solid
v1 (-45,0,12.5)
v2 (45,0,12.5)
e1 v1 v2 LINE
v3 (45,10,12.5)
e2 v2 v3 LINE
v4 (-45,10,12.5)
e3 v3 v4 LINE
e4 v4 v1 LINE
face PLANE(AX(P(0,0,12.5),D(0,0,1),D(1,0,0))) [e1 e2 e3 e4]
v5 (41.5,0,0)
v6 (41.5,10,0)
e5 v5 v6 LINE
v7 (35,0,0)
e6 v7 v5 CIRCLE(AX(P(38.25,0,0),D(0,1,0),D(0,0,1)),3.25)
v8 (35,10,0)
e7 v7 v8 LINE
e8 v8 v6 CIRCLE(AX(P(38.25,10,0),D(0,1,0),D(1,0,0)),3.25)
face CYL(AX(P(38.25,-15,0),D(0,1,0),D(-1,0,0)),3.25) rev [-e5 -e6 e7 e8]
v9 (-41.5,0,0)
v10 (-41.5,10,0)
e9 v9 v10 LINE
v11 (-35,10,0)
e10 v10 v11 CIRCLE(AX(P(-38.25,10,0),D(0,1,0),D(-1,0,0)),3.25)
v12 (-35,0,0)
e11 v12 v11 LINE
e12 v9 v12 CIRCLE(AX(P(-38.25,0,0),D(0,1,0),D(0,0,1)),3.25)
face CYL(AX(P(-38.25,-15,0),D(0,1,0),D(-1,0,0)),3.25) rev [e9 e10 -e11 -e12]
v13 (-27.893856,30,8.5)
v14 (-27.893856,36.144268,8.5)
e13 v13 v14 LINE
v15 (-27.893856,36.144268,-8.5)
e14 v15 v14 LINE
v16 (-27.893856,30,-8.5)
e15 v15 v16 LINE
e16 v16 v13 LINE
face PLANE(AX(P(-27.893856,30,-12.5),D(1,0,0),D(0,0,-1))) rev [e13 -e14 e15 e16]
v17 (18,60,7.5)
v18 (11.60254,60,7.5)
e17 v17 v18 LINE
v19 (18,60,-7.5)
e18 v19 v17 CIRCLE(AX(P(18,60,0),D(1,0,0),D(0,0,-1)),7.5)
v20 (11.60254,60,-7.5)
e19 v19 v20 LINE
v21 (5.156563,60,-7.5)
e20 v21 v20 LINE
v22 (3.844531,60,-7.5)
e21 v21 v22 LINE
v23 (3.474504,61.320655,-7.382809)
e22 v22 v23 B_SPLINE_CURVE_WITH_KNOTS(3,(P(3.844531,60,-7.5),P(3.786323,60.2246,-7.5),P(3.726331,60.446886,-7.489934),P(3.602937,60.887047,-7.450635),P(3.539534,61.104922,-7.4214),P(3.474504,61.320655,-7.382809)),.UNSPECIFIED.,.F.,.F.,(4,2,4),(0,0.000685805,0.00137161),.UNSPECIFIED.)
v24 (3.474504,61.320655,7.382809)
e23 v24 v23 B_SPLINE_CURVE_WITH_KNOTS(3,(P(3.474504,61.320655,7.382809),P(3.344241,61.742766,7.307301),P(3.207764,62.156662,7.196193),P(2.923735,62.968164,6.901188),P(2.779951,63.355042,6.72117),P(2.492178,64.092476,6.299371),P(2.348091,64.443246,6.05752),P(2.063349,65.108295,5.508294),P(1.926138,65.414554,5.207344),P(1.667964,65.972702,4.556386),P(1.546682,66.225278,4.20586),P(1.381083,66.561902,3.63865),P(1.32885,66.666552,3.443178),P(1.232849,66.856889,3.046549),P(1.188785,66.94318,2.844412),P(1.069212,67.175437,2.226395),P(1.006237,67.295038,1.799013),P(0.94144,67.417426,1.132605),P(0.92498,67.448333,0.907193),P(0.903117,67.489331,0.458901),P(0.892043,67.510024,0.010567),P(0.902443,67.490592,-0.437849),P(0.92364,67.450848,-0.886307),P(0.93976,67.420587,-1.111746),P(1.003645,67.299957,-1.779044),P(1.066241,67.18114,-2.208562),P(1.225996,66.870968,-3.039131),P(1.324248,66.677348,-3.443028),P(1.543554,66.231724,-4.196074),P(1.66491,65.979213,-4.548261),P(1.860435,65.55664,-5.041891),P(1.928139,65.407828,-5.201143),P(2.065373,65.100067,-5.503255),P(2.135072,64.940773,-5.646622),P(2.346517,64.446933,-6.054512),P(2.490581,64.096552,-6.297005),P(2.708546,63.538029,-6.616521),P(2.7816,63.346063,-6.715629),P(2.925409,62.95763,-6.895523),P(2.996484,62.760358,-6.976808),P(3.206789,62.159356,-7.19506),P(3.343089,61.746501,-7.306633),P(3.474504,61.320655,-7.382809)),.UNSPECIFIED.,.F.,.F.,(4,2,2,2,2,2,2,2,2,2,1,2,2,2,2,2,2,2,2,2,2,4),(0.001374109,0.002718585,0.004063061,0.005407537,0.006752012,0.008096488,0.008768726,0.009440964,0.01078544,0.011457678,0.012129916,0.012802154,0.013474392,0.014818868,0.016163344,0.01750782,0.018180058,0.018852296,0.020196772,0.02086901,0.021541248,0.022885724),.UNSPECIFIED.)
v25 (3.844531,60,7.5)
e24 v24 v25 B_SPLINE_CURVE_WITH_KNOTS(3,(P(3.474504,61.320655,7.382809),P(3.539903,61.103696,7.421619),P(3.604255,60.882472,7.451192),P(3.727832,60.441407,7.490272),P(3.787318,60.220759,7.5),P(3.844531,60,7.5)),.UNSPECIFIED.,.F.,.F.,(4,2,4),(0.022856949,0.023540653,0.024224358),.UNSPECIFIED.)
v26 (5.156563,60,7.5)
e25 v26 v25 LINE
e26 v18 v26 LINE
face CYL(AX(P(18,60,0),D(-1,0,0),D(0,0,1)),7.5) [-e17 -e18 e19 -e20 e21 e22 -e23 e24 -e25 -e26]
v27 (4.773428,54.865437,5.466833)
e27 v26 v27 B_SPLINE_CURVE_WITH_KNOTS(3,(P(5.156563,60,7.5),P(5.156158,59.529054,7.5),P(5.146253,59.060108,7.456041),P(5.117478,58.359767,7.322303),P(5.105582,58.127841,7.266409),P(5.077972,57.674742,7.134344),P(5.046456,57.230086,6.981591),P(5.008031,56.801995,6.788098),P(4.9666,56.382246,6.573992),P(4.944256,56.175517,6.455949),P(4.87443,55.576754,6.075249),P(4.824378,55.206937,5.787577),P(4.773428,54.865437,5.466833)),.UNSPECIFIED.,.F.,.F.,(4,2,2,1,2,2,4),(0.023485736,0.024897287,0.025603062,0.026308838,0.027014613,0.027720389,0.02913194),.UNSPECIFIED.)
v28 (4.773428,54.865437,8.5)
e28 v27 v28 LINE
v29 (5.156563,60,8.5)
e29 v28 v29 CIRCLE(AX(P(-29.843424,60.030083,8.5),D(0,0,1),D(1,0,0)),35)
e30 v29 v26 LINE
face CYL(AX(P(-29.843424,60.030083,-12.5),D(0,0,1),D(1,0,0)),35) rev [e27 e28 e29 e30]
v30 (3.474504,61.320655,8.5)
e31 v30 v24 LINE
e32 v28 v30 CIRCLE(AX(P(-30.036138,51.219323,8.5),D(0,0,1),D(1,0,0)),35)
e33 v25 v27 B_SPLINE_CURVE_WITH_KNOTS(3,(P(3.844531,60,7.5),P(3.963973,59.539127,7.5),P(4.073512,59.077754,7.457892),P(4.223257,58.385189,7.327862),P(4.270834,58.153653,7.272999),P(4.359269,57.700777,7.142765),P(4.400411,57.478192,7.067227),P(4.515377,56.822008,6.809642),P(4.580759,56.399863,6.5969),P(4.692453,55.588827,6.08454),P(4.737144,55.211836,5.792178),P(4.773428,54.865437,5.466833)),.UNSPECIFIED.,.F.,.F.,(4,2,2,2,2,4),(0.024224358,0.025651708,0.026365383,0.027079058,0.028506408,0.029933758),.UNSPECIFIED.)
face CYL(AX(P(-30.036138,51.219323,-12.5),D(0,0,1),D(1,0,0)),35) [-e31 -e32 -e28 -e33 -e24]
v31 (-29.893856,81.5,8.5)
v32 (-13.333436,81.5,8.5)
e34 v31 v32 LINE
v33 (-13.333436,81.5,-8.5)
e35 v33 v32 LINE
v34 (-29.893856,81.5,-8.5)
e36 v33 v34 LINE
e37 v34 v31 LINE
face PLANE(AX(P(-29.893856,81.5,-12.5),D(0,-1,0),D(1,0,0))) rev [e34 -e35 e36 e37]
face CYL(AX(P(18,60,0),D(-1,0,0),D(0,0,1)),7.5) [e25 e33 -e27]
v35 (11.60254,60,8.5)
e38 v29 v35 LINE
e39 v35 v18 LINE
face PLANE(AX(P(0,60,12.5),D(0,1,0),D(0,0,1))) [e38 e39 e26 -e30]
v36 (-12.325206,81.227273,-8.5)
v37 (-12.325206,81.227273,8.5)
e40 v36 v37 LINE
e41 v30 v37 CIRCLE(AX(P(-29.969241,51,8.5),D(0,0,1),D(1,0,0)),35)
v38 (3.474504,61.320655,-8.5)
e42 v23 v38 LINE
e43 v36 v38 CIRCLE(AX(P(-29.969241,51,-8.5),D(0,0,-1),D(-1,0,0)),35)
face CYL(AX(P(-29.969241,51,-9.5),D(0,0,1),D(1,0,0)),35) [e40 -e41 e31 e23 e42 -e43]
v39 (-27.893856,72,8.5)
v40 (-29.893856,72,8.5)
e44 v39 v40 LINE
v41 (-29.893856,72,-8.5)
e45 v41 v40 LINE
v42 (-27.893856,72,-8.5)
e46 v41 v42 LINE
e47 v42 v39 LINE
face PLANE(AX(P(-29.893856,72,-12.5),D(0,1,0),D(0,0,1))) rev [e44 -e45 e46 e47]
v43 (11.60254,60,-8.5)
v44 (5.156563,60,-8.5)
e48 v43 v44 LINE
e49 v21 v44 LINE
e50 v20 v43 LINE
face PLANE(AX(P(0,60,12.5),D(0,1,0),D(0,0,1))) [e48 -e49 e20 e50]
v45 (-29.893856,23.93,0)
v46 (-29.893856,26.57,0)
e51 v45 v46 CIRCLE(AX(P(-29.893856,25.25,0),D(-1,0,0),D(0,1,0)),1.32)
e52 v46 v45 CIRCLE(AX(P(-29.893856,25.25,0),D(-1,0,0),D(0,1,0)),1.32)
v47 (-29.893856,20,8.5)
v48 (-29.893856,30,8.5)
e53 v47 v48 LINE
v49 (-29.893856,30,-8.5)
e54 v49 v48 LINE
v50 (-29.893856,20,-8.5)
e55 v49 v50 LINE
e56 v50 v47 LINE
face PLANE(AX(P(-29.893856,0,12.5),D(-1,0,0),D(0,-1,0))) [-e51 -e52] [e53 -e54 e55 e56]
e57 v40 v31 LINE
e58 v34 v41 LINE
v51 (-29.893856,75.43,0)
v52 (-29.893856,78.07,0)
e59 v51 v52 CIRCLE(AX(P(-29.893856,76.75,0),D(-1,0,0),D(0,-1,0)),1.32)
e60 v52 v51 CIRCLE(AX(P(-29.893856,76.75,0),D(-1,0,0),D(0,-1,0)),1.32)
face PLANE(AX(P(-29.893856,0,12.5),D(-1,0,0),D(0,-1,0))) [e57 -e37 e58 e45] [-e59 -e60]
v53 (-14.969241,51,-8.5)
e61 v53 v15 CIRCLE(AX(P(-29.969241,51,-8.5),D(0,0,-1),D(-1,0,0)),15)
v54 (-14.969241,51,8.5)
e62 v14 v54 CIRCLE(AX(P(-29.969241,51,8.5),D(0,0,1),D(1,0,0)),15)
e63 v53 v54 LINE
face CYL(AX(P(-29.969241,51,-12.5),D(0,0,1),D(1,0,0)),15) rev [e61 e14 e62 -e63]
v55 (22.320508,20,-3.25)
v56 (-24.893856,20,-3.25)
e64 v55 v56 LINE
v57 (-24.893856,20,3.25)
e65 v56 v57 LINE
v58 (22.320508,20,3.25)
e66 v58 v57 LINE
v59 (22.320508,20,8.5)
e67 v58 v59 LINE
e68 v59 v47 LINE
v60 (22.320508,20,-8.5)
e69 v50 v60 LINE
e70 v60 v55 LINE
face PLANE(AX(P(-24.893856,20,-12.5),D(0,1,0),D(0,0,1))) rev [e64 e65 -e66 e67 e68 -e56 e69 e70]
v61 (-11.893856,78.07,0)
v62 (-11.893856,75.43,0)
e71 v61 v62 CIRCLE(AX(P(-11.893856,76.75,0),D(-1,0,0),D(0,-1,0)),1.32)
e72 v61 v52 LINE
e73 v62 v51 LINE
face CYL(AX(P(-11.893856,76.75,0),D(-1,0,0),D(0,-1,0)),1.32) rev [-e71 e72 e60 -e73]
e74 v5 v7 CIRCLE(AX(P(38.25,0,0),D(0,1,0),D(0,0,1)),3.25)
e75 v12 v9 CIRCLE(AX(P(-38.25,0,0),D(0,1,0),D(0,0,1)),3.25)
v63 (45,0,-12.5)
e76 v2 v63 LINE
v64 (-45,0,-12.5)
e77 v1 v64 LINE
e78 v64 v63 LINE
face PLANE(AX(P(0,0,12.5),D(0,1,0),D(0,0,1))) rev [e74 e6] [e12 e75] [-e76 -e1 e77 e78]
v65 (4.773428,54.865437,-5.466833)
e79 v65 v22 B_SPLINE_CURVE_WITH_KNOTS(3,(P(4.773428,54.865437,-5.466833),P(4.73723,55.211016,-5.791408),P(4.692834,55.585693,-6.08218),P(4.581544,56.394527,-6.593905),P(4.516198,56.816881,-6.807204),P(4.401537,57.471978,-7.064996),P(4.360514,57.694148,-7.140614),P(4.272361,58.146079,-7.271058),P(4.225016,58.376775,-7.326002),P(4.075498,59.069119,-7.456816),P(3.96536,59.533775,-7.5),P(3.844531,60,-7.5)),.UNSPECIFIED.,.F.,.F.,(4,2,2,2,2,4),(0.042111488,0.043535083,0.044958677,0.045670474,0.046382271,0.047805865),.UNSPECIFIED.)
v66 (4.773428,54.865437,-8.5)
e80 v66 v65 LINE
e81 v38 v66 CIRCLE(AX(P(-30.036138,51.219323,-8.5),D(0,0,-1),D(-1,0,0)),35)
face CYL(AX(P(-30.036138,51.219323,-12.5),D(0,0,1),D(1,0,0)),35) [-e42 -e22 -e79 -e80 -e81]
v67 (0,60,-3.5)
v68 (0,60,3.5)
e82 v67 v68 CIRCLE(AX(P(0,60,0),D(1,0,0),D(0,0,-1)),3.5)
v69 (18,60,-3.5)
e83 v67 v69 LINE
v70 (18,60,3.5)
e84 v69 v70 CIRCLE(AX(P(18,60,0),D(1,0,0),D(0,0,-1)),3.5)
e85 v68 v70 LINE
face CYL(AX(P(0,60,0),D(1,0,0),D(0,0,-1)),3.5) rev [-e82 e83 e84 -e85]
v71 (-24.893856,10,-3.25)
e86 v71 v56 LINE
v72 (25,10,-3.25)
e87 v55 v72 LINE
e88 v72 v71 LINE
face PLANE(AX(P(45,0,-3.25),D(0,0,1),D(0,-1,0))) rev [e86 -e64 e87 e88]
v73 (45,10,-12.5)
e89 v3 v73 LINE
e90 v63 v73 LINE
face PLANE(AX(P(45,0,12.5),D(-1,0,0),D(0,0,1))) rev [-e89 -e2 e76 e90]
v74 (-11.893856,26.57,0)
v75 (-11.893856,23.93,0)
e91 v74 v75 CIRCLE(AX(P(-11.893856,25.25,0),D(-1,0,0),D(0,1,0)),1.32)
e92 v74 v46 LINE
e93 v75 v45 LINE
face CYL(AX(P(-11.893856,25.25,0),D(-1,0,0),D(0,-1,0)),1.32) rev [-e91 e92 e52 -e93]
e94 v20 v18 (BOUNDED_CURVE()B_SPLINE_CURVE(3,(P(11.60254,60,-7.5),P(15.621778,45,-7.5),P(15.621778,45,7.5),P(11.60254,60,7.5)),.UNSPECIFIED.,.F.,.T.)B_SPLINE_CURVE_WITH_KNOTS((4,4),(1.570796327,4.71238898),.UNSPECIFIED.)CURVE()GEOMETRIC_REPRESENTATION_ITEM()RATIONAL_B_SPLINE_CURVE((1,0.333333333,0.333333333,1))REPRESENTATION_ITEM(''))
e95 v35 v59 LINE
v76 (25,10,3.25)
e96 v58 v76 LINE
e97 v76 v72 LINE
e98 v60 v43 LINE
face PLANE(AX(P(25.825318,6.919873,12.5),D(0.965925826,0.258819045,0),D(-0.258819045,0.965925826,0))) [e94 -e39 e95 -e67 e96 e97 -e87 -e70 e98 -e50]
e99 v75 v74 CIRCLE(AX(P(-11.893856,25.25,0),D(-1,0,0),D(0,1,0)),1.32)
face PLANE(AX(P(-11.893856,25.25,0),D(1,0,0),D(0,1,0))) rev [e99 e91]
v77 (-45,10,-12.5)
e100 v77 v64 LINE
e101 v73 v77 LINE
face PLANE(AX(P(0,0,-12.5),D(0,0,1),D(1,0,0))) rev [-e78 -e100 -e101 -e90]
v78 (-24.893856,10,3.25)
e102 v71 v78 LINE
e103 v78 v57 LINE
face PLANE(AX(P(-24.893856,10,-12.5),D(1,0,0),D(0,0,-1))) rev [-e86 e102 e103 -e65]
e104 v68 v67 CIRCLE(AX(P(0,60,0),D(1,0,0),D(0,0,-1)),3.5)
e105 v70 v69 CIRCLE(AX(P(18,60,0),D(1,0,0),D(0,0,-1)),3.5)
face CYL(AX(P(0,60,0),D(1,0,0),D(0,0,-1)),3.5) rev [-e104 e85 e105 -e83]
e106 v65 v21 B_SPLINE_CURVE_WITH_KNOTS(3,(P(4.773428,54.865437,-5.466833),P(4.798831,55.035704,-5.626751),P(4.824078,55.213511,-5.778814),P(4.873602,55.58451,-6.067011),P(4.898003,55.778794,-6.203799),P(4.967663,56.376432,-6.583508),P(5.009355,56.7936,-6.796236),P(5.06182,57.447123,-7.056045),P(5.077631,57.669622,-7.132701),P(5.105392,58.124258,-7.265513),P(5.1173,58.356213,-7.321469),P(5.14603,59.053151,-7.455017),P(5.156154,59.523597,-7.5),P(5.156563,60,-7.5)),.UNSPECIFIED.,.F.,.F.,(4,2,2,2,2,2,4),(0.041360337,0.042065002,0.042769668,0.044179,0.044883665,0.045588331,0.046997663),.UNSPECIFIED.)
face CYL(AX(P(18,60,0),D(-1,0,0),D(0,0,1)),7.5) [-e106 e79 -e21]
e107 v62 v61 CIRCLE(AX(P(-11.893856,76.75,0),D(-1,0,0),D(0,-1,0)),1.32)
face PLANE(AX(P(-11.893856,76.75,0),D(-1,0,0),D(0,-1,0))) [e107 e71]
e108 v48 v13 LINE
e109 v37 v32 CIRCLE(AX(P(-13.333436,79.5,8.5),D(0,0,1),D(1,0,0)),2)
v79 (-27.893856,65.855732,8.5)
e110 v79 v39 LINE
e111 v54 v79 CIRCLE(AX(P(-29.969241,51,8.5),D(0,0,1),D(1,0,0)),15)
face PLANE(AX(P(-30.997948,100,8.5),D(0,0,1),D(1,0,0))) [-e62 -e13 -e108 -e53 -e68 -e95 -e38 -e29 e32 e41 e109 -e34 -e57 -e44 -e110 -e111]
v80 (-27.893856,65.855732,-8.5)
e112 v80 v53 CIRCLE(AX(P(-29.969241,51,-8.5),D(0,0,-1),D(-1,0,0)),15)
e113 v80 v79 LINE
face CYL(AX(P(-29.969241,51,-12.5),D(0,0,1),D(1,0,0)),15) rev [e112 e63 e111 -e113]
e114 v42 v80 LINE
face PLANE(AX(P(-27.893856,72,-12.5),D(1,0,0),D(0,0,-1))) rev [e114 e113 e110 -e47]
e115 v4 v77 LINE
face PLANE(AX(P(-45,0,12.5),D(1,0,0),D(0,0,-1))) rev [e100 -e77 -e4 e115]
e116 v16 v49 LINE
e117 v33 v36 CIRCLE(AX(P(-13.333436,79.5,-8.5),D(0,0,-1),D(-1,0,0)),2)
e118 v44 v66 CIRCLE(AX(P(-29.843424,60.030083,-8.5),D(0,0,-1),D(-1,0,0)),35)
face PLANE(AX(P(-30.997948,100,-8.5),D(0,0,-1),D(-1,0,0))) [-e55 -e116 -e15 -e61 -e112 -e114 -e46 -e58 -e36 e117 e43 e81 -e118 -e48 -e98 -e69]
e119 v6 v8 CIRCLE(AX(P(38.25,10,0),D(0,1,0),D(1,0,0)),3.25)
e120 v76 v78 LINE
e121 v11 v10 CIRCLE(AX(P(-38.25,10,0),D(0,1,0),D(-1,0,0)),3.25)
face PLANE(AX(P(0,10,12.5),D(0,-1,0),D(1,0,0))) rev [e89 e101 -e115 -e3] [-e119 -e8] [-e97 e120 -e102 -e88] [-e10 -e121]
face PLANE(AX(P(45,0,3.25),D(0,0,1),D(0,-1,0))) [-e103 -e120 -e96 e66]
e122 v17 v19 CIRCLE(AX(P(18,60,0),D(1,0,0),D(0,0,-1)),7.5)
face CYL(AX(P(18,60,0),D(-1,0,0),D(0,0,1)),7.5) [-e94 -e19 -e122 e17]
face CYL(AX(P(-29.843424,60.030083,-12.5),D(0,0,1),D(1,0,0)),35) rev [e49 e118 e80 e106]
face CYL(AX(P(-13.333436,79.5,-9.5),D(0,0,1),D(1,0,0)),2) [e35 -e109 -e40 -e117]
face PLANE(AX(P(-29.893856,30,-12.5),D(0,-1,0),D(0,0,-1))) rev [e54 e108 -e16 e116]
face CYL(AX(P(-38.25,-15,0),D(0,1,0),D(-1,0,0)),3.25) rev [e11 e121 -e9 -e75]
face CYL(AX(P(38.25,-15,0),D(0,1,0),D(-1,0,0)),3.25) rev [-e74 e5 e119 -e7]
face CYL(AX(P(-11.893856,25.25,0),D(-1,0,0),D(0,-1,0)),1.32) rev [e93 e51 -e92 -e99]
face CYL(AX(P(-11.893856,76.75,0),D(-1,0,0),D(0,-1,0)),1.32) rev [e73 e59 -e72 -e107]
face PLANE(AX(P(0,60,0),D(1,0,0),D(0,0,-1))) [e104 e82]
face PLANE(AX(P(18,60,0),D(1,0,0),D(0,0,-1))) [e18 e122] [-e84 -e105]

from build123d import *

# Parameters (mm, degrees)
BRACKET_PROFILE_SKETCH_W     = 5
BRACKET_PROFILE_SKETCH_H     = 10
BRACKET_BODY_DEPTH           = 12.5
SPLIT_SLOT_SKETCH_R          = 3.25
SPLIT_SLOT_CUT_DEPTH         = 25
SIDE_TRIM_SKETCH_W           = 61.995895312
SIDE_TRIM_SKETCH_H           = 4
SIDE_TRIM_CUT_DEPTH          = 100
BASE_PLATE_SKETCH_W          = 61.995895312
BASE_PLATE_SKETCH_H          = 4
BASE_PLATE_DEPTH             = 10
UPRIGHT_STEP_CUT_DEPTH       = 104.780787142
UPRIGHT_RELIEF_SKETCH_W      = 5
UPRIGHT_RELIEF_SKETCH_H      = 10
UPRIGHT_RELIEF_CUT_DEPTH     = 96.437152095
RELIEF_NOTCH_A_SKETCH_W      = 5.25
RELIEF_NOTCH_A_SKETCH_H      = 10
RELIEF_NOTCH_A_DEPTH         = 109.090938874
RELIEF_NOTCH_B_SKETCH_W      = 5.25
RELIEF_NOTCH_B_SKETCH_H      = 10
RELIEF_NOTCH_B_DEPTH         = 109.090938874
BEARING_SEAT_CUT_DEPTH       = 96.437152095
SEAT_GROOVE_A_SKETCH_R       = 1.32
SEAT_GROOVE_A_DEPTH          = 18
SEAT_GROOVE_B_DEPTH          = 18
SIDE_BOSS_SKETCH_R           = 7.5
SIDE_BOSS_DEPTH              = 18
SIDE_BOSS_BORE_SKETCH_R      = 3.5
SIDE_BOSS_BORE_DEPTH         = 18
FACE_RECESS_CUT_DEPTH        = 94.933487193
FACE_RECESS_CUT_DEPTH_BACK   = 94.933487193
SIDE_SLOT_CUT_DEPTH          = 5
BOSS_EXTENSION_SKETCH_R      = 7.5
BOSS_EXTENSION_DEPTH         = 18
BOSS_EXTENSION_BORE_SKETCH_R = 3.5
BOSS_EXTENSION_BORE_DEPTH    = 18


with BuildPart() as part:
    # Bracket Profile Sketch → Bracket Body (new, symmetric)
    with BuildSketch(Plane.XY):
        Polygon((-45, 10), (-45, 0), (0, 0), (45, 0), (45, 10), align=None)
        with BuildLine():
            Line((-13.893855715, 10), (25, 10))
            Line((25, 10), (11.602540378, 60))
            Line((11.602540378, 60), (5.106144285, 60))
            ThreePointArc((5.106144285, 60), (-0.019117223, 41.765417471), (-13.893855715, 28.871235167))
            Line((-13.893855715, 28.871235167), (-13.893855715, 10))
        make_face()
        Polygon((-24.893855715, 10), (-13.893855715, 10), (-13.893855715, 28.871235167), (-29.893855715, 29), (-29.893855715, 20), (-24.893855715, 20), align=None)
        with Locations((-27.393855715, 15)):
            Rectangle(BRACKET_PROFILE_SKETCH_W, BRACKET_PROFILE_SKETCH_H)
        with BuildLine():
            Line((-13.893855715, 41), (-13.893855715, 28.871235167))
            ThreePointArc((-13.893855715, 28.871235167), (-0.019117223, 41.765417471), (5.106144285, 60))
            ThreePointArc((5.106144285, 60), (-0.019117223, 78.234582529), (-13.893855715, 91.128764833))
            Line((-13.893855715, 91.128764833), (-13.893855715, 79))
            Line((-13.893855715, 79), (-6.677482183, 79))
            ThreePointArc((-6.677482183, 79), (0.106144285, 60), (-6.677482183, 41))
            Line((-6.677482183, 41), (-13.893855715, 41))
        make_face()
        Polygon((-29.893855715, 29), (-13.893855715, 28.871235167), (-13.893855715, 41), (-27.893855715, 41), (-27.893855715, 39), (-29.893855715, 39), align=None)
        with BuildLine():
            Line((-27.893855715, 41), (-13.893855715, 41))
            Line((-13.893855715, 41), (-13.893855715, 79))
            Line((-13.893855715, 79), (-27.893855715, 79))
            Line((-27.893855715, 79), (-27.893855715, 74.866068747))
            ThreePointArc((-27.893855715, 74.866068747), (-14.893855715, 60), (-27.893855715, 45.133931253))
            Line((-27.893855715, 45.133931253), (-27.893855715, 41))
        make_face()
        with BuildLine():
            Line((-13.893855715, 79), (-13.893855715, 41))
            Line((-13.893855715, 41), (-6.677482183, 41))
            ThreePointArc((-6.677482183, 41), (0.106144285, 60), (-6.677482183, 79))
            Line((-6.677482183, 79), (-13.893855715, 79))
        make_face()
        with BuildLine():
            Line((-29.893855715, 60), (-29.893855715, 39))
            Line((-29.893855715, 39), (-27.893855715, 39))
            Line((-27.893855715, 39), (-27.893855715, 41))
            Line((-27.893855715, 41), (-27.893855715, 45.133931253))
            ThreePointArc((-27.893855715, 45.133931253), (-14.893855715, 60), (-27.893855715, 74.866068747))
            Line((-27.893855715, 74.866068747), (-27.893855715, 79))
            Line((-27.893855715, 79), (-27.893855715, 81))
            Line((-27.893855715, 81), (-29.893855715, 81))
            Line((-29.893855715, 81), (-29.893855715, 79))
            Line((-29.893855715, 79), (-29.893855715, 60))
        make_face()
        Polygon((-13.893855715, 79), (-13.893855715, 91.128764833), (-29.893855715, 91), (-29.893855715, 81), (-27.893855715, 81), (-27.893855715, 79), align=None)
    extrude(amount=BRACKET_BODY_DEPTH, both=True)

    # Split Slot Sketch → Split Slot Cut (cut)
    with BuildSketch(Plane(origin=(0, 10, 0), x_dir=(1, 0, 0), z_dir=(0, 1, 0))):
        with Locations(Location((-38.25, 0, 0), (0, 0, 180))):
            Circle(SPLIT_SLOT_SKETCH_R)
        with Locations(Location((38.25, 0, 0), (0, 0, 270))):
            Circle(SPLIT_SLOT_SKETCH_R)
    extrude(amount=-SPLIT_SLOT_CUT_DEPTH, mode=Mode.SUBTRACT)

    # Side Trim Sketch → Side Trim Cut (cut)
    with BuildSketch(Plane(origin=(0, 0, 0), x_dir=(1, 0, 0), z_dir=(0, 1, 0))):
        with Locations((0, 10.5)):
            Rectangle(SIDE_TRIM_SKETCH_W, SIDE_TRIM_SKETCH_H)
        with Locations((0, -10.5)):
            Rectangle(SIDE_TRIM_SKETCH_W, SIDE_TRIM_SKETCH_H)
    extrude(amount=SIDE_TRIM_CUT_DEPTH, mode=Mode.SUBTRACT)

    # Base Plate Sketch → Base Plate (add)
    with BuildSketch(Plane(origin=(0, 0, 0), x_dir=(1, 0, 0), z_dir=(0, 1, 0))):
        with Locations((0, 10.5)):
            Rectangle(BASE_PLATE_SKETCH_W, BASE_PLATE_SKETCH_H)
        with Locations((0, -10.5)):
            Rectangle(BASE_PLATE_SKETCH_W, BASE_PLATE_SKETCH_H)
    extrude(amount=BASE_PLATE_DEPTH)

    # Upright Step Sketch → Upright Step Cut (cut, through all)
    with BuildSketch(Plane.XY.offset(8.5)):
        with BuildLine():
            Line((-29.893855715, 81.5), (-2.275926756, 81.5))
            ThreePointArc((-2.275926756, 81.5), (-7.559818693, 86.947927384), (-13.893855715, 91.128764833))
            Line((-13.893855715, 91.128764833), (-29.893855715, 91))
            Line((-29.893855715, 91), (-29.893855715, 81.5))
        make_face()
    extrude(amount=-UPRIGHT_STEP_CUT_DEPTH, mode=Mode.SUBTRACT)

    # Upright Relief Sketch → Upright Relief Cut (cut, through all)
    with BuildSketch(Plane.XY.offset(8.5)):
        with Locations((-27.393855715, 15)):
            Rectangle(UPRIGHT_RELIEF_SKETCH_W, UPRIGHT_RELIEF_SKETCH_H)
    extrude(amount=-UPRIGHT_RELIEF_CUT_DEPTH, mode=Mode.SUBTRACT)

    # Relief Notch A Sketch → Relief Notch A (cut, through all)
    with BuildSketch(Plane.ZY.offset(24.893855715)):
        with Locations((5.875, 15)):
            Rectangle(RELIEF_NOTCH_A_SKETCH_W, RELIEF_NOTCH_A_SKETCH_H)
    extrude(amount=-RELIEF_NOTCH_A_DEPTH, mode=Mode.SUBTRACT)

    # Relief Notch B Sketch → Relief Notch B (cut, through all)
    with BuildSketch(Plane.ZY.offset(24.893855715)):
        with Locations((-5.875, 15)):
            Rectangle(RELIEF_NOTCH_B_SKETCH_W, RELIEF_NOTCH_B_SKETCH_H)
    extrude(amount=-RELIEF_NOTCH_B_DEPTH, mode=Mode.SUBTRACT)

    # Bearing Seat Sketch → Bearing Seat Cut (cut, through all)
    with BuildSketch(Plane.XY.offset(8.5)):
        with BuildLine():
            Line((-29.969241256, 51), (-29.893855715, 30))
            Line((-29.893855715, 30), (-27.893855715, 30))
            Line((-27.893855715, 30), (-27.893855715, 36.144267946))
            ThreePointArc((-27.893855715, 36.144267946), (-14.969241256, 51), (-27.893855715, 65.855732054))
            Line((-27.893855715, 65.855732054), (-27.893855715, 72))
            Line((-27.893855715, 72), (-29.893855715, 72))
            Line((-29.893855715, 72), (-29.969241256, 51))
        make_face()
    extrude(amount=-BEARING_SEAT_CUT_DEPTH, mode=Mode.SUBTRACT)

    # Seat Groove A Sketch → Seat Groove A (cut)
    with BuildSketch(Plane.ZY.offset(29.893855715)):
        with Locations(Location((0, 76.75, 0), (0, 0, 270))):
            Circle(SEAT_GROOVE_A_SKETCH_R)
        with Locations(Location((0, 25.25, 0), (0, 0, 90))):
            Circle(SEAT_GROOVE_A_SKETCH_R)
    extrude(amount=-SEAT_GROOVE_A_DEPTH, mode=Mode.SUBTRACT)

    # Seat Groove B Sketch → Seat Groove B (cut)
    with BuildSketch(Plane.XY.offset(8.5)):
        with BuildLine():
            Line((-2.275926756, 81.5), (-13.333436496, 81.5))
            ThreePointArc((-13.333436496, 81.5), (-12.811203529, 81.430614598), (-12.325205905, 81.227272727))
            ThreePointArc((-12.325205905, 81.227272727), (-0.84803662, 70.415340341), (4.718757235, 55.662913324))
            ThreePointArc((4.718757235, 55.662913324), (3.788925867, 69.276539885), (-2.275926756, 81.5))
        make_face()
    extrude(amount=-SEAT_GROOVE_B_DEPTH, mode=Mode.SUBTRACT)

    # Side Boss Sketch → Side Boss (add)
    with BuildSketch(Plane(origin=(0, 0, 0), x_dir=(0, 0, -1), z_dir=(1, 0, 0))):
        with Locations((0, 60)):
            Circle(SIDE_BOSS_SKETCH_R)
    extrude(amount=SIDE_BOSS_DEPTH)

    # Side Boss Bore Sketch → Side Boss Bore (cut)
    with BuildSketch(Plane(origin=(18, 0, 0), x_dir=(0, 0, -1), z_dir=(1, 0, 0))):
        with Locations((0, 60)):
            Circle(SIDE_BOSS_BORE_SKETCH_R)
    extrude(amount=-SIDE_BOSS_BORE_DEPTH, mode=Mode.SUBTRACT)

    # Face Recess Sketch → Face Recess Cut (cut, two sides: drawn at the far end of the back side and taken through both)
    with BuildSketch(Plane.XY.offset(-FACE_RECESS_CUT_DEPTH_BACK)):
        with BuildLine():
            Line((-1.830885875, 81.013355064), (-12.010951395, 81.22086692))
            ThreePointArc((-12.010951395, 81.22086692), (-0.514451936, 70.02012246), (4.773427937, 54.865436626))
            ThreePointArc((4.773427937, 54.865436626), (4.090902797, 68.60104967), (-1.830885875, 81.013355064))
        make_face()
    extrude(amount=FACE_RECESS_CUT_DEPTH + FACE_RECESS_CUT_DEPTH_BACK, mode=Mode.SUBTRACT)


with BuildPart() as face_recess_cut_piece_1:
    # of the separate pieces the step leaves, piece 1, a body of its own (face_recess_cut_pieces)
    add(part.part.solids().sort_by_distance((-45, 10, -12.5))[0])

    # Boss Extension Sketch → Boss Extension (add)
    with BuildSketch(Plane(origin=(18, 0, 0), x_dir=(0, 0, -1), z_dir=(1, 0, 0))):
        with Locations((0, 60)):
            Circle(BOSS_EXTENSION_SKETCH_R)
    extrude(amount=-BOSS_EXTENSION_DEPTH)

    # Boss Extension Bore Sketch → Boss Extension Bore (cut)
    with BuildSketch(Plane(origin=(18, 0, 0), x_dir=(0, 0, -1), z_dir=(1, 0, 0))):
        with Locations((0, 60)):
            Circle(BOSS_EXTENSION_BORE_SKETCH_R)
    extrude(amount=-BOSS_EXTENSION_BORE_DEPTH, mode=Mode.SUBTRACT)


with BuildPart() as face_recess_cut_piece_2:
    # of the separate pieces the step leaves, piece 2, a body of its own (face_recess_cut_pieces)
    add(part.part.solids().sort_by_distance((-1.905011421, 81.014866049, 8.5))[0])

    # Side Slot Sketch → Side Slot Cut (cut)
    with BuildSketch(Plane(origin=(0, 0, 0), x_dir=(0, 0, -1), z_dir=(1, 0, 0))):
        Polygon((8.5, 81.5), (-8.5, 81.5), (-8.5, 81.014866049), (8.5, 81.014866049), (8.5, 81.227272727), align=None)
    extrude(amount=-SIDE_SLOT_CUT_DEPTH, mode=Mode.SUBTRACT)


solid = face_recess_cut_piece_1.part
